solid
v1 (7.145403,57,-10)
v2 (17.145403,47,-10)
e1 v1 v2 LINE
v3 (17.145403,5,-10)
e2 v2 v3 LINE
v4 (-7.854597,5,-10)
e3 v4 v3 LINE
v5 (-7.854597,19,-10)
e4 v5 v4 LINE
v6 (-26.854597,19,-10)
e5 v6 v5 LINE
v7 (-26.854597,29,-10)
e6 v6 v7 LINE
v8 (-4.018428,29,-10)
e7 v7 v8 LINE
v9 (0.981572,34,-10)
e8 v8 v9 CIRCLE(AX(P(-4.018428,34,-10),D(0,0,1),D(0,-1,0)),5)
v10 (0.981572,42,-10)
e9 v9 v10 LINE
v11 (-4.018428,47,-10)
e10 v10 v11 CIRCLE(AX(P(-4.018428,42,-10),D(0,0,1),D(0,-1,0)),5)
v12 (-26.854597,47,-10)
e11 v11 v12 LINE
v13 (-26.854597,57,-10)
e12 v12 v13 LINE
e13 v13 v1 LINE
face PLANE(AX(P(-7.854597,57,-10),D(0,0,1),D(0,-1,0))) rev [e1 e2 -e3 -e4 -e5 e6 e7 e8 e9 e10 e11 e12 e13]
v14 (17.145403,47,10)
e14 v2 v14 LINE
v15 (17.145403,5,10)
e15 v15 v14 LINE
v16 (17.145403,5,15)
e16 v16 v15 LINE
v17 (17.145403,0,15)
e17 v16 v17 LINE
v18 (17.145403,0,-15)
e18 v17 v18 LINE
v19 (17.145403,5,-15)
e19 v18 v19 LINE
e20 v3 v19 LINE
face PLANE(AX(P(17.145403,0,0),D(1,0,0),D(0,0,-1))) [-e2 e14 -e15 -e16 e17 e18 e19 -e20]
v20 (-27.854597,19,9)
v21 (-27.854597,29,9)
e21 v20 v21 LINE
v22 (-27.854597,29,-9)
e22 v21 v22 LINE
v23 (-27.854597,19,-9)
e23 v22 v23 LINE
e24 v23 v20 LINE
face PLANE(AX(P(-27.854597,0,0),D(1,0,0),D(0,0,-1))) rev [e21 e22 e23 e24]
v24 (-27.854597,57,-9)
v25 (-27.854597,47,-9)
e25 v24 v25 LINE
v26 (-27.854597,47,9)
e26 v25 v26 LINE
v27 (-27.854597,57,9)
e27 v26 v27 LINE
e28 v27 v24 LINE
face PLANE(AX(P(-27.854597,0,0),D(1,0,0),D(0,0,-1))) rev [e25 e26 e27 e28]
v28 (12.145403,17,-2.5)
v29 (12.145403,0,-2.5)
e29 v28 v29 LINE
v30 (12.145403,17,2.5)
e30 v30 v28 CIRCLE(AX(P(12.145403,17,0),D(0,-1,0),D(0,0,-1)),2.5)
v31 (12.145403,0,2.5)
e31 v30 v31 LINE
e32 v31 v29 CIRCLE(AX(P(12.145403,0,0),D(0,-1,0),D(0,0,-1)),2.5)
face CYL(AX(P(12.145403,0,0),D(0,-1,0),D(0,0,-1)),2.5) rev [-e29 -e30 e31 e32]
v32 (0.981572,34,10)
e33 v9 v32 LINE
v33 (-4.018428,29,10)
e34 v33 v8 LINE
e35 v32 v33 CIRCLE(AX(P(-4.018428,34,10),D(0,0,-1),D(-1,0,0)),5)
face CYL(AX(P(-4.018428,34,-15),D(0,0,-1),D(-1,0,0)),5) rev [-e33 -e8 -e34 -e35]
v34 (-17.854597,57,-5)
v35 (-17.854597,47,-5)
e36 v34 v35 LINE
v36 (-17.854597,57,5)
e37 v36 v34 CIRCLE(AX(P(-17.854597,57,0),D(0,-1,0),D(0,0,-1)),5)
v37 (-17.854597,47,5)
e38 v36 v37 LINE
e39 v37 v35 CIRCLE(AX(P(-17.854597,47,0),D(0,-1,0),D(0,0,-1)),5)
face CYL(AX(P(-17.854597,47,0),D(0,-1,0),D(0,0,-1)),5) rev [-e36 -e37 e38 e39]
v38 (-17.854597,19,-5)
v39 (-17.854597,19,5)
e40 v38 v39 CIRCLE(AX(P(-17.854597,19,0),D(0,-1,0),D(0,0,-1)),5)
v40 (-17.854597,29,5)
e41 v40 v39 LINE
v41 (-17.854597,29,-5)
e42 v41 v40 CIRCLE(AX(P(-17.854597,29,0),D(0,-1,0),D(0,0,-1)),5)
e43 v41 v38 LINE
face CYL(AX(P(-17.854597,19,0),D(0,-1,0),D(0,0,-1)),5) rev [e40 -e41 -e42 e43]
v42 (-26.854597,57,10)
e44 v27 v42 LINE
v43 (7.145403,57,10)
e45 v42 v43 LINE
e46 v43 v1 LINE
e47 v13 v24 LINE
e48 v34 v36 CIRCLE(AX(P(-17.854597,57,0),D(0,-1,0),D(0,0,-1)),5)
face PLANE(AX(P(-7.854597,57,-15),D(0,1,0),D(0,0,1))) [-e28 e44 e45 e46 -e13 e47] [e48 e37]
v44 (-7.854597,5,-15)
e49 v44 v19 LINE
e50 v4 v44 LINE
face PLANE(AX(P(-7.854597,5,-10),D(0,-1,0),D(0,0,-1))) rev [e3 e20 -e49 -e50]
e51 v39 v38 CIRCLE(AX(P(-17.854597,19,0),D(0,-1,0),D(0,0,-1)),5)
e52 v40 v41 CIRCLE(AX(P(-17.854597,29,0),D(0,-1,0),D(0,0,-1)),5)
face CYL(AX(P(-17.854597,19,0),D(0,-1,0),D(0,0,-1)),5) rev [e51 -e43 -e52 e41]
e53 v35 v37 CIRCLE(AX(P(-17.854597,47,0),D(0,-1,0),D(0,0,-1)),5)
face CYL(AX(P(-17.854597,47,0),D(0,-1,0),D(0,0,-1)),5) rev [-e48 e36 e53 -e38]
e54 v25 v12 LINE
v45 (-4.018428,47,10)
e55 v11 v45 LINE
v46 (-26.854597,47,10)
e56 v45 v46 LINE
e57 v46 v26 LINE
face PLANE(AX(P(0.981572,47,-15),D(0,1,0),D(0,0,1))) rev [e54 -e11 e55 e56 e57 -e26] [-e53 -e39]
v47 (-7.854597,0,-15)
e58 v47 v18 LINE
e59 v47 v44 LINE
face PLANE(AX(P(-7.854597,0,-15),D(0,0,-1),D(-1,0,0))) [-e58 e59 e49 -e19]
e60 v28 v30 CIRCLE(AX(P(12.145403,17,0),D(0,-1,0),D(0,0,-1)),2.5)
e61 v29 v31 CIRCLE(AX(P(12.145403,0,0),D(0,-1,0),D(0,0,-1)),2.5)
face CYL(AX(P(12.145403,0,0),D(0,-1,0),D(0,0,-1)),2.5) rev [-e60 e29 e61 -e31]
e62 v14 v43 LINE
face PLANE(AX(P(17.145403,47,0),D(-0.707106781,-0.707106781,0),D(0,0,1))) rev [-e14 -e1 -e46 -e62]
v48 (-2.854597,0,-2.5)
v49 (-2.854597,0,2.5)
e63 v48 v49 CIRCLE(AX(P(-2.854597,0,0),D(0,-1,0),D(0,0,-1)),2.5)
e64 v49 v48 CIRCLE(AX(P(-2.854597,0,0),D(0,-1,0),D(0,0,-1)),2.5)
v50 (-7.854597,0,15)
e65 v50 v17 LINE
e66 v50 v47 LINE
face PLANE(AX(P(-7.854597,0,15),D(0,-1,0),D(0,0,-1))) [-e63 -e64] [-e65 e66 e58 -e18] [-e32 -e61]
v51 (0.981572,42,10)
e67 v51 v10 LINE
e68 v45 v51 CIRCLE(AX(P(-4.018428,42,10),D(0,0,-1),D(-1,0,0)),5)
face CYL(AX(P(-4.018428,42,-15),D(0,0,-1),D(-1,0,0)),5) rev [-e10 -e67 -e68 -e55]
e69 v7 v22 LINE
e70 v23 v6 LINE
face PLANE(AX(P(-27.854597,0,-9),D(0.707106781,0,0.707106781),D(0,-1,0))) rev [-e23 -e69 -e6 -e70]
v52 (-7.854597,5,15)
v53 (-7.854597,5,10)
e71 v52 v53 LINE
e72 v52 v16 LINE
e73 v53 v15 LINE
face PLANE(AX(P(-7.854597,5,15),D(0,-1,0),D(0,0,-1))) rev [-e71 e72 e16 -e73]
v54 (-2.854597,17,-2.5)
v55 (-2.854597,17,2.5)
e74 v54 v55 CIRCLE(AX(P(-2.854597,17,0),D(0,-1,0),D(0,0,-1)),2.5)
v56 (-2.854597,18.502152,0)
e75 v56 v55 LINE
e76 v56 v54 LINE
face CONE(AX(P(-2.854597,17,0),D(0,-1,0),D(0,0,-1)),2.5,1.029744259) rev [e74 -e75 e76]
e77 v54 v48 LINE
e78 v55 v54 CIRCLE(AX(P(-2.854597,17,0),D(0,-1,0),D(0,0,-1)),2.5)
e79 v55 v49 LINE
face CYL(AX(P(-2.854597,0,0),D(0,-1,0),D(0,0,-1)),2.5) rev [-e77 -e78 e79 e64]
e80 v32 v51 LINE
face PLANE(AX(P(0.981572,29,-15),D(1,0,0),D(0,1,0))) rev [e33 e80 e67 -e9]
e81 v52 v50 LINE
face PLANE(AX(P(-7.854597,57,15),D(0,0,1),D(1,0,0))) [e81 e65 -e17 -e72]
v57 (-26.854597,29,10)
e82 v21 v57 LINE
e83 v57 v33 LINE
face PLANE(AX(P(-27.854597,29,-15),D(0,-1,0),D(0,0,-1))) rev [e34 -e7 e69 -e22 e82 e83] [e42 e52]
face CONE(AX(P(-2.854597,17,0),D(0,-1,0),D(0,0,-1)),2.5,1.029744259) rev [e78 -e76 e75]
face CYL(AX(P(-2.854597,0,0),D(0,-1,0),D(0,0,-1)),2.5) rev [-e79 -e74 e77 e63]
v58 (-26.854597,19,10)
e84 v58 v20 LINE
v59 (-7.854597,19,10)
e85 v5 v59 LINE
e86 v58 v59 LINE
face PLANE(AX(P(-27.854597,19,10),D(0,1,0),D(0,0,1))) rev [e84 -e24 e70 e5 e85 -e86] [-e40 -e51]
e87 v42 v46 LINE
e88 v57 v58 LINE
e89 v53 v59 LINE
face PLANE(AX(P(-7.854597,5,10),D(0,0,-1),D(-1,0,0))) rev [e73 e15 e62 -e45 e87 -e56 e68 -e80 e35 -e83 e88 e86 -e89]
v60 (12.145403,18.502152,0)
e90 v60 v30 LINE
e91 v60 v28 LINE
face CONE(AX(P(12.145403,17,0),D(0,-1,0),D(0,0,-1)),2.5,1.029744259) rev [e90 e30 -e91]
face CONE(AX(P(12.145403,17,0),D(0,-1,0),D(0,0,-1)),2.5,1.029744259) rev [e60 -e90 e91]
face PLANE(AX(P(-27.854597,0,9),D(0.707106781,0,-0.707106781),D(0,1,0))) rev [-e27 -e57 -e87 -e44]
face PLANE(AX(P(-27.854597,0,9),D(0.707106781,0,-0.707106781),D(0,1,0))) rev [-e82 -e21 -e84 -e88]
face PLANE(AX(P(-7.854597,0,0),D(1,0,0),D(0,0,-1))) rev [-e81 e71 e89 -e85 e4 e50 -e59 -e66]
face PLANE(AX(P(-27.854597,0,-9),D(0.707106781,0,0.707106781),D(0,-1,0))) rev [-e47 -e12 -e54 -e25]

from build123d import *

# Parameters (mm, degrees)
SKETCH_1_W                  = 30
SKETCH_1_H                  = 57
EXTRUDE_1_DEPTH             = 25
SKETCH_2_W                  = 5
SKETCH_2_H                  = 52
CUT_EXTRUDE_1_DEPTH         = 65.02343321
SKETCH_3_W                  = 5
SKETCH_3_H                  = 52
CUT_EXTRUDE_2_DEPTH         = 65.02343321
SKETCH_4_W                  = 20
SKETCH_4_H                  = 38
EXTRUDE_2_DEPTH             = 20
SKETCH_5_W                  = 28.836169251
SKETCH_5_H                  = 18
CUT_EXTRUDE_3_DEPTH         = 69.190018281
HOLE_WIZARD_10_0_10_1_D     = 10
HOLE_WIZARD_10_0_10_1_DEPTH = 10
HOLE_WIZARD_10_0_10_2_D     = 10
HOLE_WIZARD_10_0_10_2_DEPTH = 38
HOLE_WIZARD_5_0_5_1_D       = 5
HOLE_WIZARD_5_0_5_1_DEPTH   = 17
HOLE_WIZARD_5_0_5_1_TIP     = 1.502151548
CHAMFER_1_SIZE              = 1
CHAMFER_2_SIZE              = 10
FILLET_1_R                  = 5


with BuildPart() as part:
    # 草图1 → 凸台-拉伸1 (new body)
    with BuildSketch(Plane(origin=(17.145402657, 0, 0), x_dir=(0, 0, -1), z_dir=(1, 0, 0))):
        with Locations((0, 28.5)):
            Rectangle(SKETCH_1_W, SKETCH_1_H)
    extrude(amount=-EXTRUDE_1_DEPTH)

    # 草图2 → 切除-拉伸1 (cut, through all)
    with BuildSketch(Plane(origin=(17.145402657, 0, 0), x_dir=(0, 0, -1), z_dir=(1, 0, 0))):
        with Locations((-12.5, 31)):
            Rectangle(SKETCH_2_W, SKETCH_2_H)
    extrude(amount=-CUT_EXTRUDE_1_DEPTH, mode=Mode.SUBTRACT)

    # 草图3 → 切除-拉伸2 (cut, through all)
    with BuildSketch(Plane(origin=(17.145402657, 0, 0), x_dir=(0, 0, -1), z_dir=(1, 0, 0))):
        with Locations((12.5, 31)):
            Rectangle(SKETCH_3_W, SKETCH_3_H)
    extrude(amount=-CUT_EXTRUDE_2_DEPTH, mode=Mode.SUBTRACT)

    # 草图4 → 凸台-拉伸2 (add)
    with BuildSketch(Plane.ZY.offset(7.854597343)):
        with Locations((0, 38)):
            Rectangle(SKETCH_4_W, SKETCH_4_H)
    extrude(amount=EXTRUDE_2_DEPTH)

    # 草图5 → 切除-拉伸3 (cut, through all)
    with BuildSketch(Plane.XY.offset(10)):
        with Locations((-13.436512718, 38)):
            Rectangle(SKETCH_5_W, SKETCH_5_H)
    extrude(amount=-CUT_EXTRUDE_3_DEPTH, mode=Mode.SUBTRACT)

    # Ø10.0 (10) 直径孔1
    with Locations(Plane(origin=(0, 47, 0), x_dir=(-1, 0, 0), z_dir=(0, -1, 0))):
        with Locations((17.854597343, 0)):
            Hole(HOLE_WIZARD_10_0_10_1_D / 2, depth=HOLE_WIZARD_10_0_10_1_DEPTH)

    # Ø10.0 (10) 直径孔2
    with Locations(Plane(origin=(0, 19, 0), x_dir=(-1, 0, 0), z_dir=(0, -1, 0))):
        with Locations((17.854597343, 0)):
            Hole(HOLE_WIZARD_10_0_10_2_D / 2, depth=HOLE_WIZARD_10_0_10_2_DEPTH)

    # Ø5.0 (5) 直径孔1
    with Locations(Plane(origin=(0, 0, 0), x_dir=(-1, 0, 0), z_dir=(0, -1, 0))):
        with Locations((2.854597343, 0), (-12.145402657, 0)):
            Hole(HOLE_WIZARD_5_0_5_1_D / 2, depth=HOLE_WIZARD_5_0_5_1_DEPTH)
            with Locations((0, 0, -(HOLE_WIZARD_5_0_5_1_DEPTH + HOLE_WIZARD_5_0_5_1_TIP / 2))):  # 118° drill point
                Cone(0, HOLE_WIZARD_5_0_5_1_D / 2, HOLE_WIZARD_5_0_5_1_TIP, mode=Mode.SUBTRACT)

    # 倒角1
    chamfer_1_edges = [part.edges().sort_by_distance(p)[0] for p in [
        (-27.854597343, 52, -10),
        (-27.854597343, 24, 10),
        (-27.854597343, 24, -10),
        (-27.854597343, 52, 10),
    ]]
    chamfer(chamfer_1_edges, length=CHAMFER_1_SIZE)

    # 倒角2
    chamfer_2_edges = [part.edges().sort_by_distance(p)[0] for p in [
        (17.145402657, 57, 0),
    ]]
    chamfer(chamfer_2_edges, length=CHAMFER_2_SIZE)

    # 圆角1
    fillet_1_edges = [part.edges().sort_by_distance(p)[0] for p in [
        (0.981571908, 47, 0),
        (0.981571908, 29, 0),
    ]]
    fillet(fillet_1_edges, radius=FILLET_1_R)


solid = part.part
